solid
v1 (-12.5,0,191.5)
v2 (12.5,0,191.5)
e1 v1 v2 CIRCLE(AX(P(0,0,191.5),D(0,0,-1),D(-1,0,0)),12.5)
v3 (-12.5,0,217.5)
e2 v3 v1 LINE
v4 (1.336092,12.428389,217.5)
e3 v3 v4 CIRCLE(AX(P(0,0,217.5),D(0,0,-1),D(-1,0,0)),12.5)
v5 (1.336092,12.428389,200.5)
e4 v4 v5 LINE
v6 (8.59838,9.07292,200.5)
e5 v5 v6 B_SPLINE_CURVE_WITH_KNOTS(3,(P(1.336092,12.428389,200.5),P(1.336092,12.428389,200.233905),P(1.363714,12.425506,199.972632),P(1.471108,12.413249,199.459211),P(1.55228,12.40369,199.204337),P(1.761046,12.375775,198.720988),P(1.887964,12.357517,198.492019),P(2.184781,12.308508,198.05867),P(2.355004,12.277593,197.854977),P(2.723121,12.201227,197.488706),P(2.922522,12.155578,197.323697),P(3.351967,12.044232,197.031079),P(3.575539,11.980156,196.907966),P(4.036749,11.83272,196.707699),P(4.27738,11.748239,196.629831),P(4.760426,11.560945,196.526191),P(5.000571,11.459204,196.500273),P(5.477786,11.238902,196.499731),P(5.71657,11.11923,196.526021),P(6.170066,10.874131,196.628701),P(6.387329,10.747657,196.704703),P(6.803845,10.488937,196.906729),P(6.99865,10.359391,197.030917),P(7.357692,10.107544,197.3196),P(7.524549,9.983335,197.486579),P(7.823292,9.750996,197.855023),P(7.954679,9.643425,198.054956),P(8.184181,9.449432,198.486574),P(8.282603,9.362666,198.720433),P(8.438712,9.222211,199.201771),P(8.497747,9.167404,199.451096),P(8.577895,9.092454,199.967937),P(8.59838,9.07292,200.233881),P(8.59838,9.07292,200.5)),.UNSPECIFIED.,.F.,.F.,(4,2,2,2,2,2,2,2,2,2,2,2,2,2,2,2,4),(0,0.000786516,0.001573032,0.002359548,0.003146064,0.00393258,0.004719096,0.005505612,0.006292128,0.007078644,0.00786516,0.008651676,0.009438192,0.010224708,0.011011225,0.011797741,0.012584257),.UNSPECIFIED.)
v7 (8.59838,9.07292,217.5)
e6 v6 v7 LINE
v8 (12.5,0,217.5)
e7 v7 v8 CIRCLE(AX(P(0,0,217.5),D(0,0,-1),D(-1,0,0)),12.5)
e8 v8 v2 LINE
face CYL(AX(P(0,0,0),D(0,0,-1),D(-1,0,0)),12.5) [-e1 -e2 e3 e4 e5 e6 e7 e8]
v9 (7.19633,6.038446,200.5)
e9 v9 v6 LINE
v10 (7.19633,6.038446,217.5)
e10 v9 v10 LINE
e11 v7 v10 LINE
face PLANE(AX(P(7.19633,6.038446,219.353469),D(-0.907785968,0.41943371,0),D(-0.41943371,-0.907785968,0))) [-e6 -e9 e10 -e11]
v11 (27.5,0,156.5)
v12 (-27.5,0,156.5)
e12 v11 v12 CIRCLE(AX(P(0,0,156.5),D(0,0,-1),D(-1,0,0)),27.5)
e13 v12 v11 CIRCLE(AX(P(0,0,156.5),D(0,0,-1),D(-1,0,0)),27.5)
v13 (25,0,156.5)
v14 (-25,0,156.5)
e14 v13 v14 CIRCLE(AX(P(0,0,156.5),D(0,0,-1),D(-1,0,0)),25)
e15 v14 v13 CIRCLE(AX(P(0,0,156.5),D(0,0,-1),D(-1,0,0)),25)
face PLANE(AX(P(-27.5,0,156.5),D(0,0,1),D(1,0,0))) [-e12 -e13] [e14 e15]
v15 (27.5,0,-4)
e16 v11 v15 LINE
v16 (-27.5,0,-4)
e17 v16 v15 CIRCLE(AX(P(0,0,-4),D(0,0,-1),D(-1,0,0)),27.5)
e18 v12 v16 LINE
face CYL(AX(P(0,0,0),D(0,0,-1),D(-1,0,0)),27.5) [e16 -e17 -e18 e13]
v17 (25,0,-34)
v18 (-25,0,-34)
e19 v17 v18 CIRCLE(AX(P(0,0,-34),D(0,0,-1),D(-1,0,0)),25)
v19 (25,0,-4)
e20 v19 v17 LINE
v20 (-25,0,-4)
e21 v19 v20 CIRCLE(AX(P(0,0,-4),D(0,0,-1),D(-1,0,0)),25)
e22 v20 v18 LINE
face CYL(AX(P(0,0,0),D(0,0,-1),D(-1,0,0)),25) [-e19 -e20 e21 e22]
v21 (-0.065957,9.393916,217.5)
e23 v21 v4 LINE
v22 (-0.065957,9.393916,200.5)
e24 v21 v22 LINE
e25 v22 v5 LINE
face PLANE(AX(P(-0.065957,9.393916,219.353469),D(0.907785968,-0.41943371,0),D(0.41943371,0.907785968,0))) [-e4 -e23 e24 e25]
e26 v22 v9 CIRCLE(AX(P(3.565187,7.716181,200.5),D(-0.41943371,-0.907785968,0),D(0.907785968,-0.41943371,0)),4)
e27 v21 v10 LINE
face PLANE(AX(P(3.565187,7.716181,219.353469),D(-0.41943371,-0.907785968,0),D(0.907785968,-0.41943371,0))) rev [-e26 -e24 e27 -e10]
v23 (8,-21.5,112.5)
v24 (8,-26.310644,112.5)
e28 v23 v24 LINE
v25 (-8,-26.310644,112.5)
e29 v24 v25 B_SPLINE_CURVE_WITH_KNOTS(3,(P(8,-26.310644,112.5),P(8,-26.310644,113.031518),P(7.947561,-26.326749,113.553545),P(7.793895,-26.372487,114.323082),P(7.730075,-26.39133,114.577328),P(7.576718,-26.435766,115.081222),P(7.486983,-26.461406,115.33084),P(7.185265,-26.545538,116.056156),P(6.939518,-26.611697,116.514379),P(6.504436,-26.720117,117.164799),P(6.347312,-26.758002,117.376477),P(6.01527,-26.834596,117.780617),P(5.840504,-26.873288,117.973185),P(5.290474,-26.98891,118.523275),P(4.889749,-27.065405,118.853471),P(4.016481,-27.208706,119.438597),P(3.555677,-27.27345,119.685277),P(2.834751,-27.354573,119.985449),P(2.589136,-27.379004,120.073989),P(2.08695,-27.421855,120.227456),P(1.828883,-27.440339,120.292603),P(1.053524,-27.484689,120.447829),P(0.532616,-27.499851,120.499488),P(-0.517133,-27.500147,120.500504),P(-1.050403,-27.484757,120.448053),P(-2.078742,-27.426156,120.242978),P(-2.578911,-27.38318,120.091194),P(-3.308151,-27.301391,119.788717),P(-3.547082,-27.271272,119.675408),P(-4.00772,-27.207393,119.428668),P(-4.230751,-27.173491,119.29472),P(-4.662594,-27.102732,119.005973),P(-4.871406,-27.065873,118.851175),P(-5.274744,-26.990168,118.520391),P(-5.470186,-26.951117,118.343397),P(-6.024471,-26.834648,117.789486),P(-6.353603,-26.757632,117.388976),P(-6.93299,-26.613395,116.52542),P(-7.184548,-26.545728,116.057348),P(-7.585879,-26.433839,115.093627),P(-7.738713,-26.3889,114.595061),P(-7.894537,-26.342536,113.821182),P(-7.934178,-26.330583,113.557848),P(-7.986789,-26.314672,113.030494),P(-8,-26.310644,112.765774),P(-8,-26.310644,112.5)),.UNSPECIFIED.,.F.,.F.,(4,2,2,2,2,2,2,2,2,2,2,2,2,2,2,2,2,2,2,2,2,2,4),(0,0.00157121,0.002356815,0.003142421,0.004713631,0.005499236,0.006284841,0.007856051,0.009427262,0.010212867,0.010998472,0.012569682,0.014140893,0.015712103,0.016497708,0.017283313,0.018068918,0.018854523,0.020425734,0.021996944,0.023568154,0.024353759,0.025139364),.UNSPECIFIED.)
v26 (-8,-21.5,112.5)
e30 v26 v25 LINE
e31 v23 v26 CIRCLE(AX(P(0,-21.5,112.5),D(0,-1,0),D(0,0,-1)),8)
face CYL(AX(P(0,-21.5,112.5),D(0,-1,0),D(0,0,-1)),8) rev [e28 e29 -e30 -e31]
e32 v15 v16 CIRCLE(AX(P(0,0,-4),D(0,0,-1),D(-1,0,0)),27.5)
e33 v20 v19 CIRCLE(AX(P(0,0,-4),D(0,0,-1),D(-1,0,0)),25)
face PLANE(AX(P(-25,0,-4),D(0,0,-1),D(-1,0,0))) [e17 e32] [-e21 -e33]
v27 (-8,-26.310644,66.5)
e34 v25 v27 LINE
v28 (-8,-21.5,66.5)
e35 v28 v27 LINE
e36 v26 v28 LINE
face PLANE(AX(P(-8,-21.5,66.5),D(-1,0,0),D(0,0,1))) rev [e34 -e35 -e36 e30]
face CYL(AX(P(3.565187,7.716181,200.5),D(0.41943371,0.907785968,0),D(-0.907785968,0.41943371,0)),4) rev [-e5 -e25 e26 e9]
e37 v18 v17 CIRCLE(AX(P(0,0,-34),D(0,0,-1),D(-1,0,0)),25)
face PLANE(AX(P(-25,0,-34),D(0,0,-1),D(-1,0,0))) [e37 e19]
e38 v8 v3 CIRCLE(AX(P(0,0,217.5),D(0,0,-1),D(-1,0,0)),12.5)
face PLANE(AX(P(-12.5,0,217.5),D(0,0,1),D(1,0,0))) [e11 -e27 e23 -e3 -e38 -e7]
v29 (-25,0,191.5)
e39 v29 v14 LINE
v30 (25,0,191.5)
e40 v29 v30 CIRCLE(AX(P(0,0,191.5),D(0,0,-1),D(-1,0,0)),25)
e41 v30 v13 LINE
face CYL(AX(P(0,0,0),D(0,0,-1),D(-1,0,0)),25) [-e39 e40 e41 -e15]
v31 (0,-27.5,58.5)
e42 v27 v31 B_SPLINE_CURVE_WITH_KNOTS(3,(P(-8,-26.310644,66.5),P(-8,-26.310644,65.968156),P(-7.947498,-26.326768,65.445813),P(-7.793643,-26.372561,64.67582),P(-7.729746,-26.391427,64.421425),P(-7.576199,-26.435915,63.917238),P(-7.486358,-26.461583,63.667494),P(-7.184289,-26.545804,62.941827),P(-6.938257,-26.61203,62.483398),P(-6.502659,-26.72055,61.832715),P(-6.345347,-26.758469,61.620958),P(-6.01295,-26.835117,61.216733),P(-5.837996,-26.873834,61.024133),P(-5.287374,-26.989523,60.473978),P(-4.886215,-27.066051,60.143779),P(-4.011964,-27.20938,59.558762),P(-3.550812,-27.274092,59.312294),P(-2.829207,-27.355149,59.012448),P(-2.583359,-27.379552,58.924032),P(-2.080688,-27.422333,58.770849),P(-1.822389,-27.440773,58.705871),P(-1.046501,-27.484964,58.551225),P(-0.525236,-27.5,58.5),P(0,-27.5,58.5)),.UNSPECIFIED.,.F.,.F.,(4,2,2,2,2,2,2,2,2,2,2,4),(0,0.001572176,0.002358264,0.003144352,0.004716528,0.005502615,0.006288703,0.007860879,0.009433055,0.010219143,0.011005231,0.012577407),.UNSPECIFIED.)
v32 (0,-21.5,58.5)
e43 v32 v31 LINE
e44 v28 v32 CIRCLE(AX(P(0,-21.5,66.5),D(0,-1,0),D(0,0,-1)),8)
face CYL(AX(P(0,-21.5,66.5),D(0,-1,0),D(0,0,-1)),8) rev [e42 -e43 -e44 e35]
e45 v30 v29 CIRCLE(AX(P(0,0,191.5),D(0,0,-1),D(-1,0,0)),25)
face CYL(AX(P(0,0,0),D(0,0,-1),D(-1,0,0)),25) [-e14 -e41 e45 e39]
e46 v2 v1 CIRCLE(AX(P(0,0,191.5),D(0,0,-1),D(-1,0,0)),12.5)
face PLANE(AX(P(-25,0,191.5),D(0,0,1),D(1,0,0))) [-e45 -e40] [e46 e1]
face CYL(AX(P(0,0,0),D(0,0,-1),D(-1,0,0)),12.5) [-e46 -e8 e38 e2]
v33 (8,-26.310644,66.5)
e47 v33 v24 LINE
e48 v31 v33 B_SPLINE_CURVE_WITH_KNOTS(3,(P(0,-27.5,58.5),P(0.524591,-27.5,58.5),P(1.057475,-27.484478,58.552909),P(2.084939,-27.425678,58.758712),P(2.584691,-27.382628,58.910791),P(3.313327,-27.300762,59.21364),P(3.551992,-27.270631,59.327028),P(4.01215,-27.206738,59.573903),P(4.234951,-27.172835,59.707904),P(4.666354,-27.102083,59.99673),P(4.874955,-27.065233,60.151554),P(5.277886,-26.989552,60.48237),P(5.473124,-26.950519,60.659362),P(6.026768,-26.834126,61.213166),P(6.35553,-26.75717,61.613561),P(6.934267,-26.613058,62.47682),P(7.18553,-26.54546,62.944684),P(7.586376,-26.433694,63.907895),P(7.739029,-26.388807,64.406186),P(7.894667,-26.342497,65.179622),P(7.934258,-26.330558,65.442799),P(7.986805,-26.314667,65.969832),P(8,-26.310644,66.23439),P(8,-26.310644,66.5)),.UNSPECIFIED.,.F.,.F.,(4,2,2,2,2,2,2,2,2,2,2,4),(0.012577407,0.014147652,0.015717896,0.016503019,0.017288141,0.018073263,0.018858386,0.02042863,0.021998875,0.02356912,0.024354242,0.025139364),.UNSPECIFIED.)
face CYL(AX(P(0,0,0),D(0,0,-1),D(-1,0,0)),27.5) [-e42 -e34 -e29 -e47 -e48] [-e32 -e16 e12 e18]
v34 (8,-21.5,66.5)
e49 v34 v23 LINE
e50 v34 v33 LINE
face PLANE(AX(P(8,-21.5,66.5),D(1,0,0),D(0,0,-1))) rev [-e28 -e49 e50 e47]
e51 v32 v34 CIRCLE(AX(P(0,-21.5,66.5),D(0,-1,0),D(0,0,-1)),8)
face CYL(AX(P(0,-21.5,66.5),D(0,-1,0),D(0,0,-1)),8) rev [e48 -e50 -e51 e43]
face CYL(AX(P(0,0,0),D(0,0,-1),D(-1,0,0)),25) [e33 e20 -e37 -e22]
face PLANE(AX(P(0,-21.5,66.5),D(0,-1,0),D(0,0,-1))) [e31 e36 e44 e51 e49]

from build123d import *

# Parameters (mm, degrees)
CUT_EXTRUDE_2_DEPTH = 6
CUT_EXTRUDE_3_DEPTH = 7.3


with BuildPart() as part:
    # 草图1 → 旋转1 (revolve)
    with BuildSketch(Plane(origin=(0, 0, 0), x_dir=(1, 0, 0), z_dir=(0, 1, 0))):
        Polygon((-25, 34), (-25, 4), (-27.5, 4), (-27.5, -156.5), (-25, -156.5), (-25, -191.5), (-12.5, -191.5), (-12.5, -217.5), (0, -217.5), (0, 34), align=None)
    revolve(axis=Axis((0, 0, 0), (0, 0, 1)))

    # 草图3 → 切除-拉伸2 (cut)
    with BuildSketch(Plane(origin=(0, -27.5, 0), x_dir=(-1, 0, 0), z_dir=(0, -1, 0))):
        with BuildLine():
            Line((8, -66.5), (8, -112.5))
            ThreePointArc((8, -112.5), (0, -120.5), (-8, -112.5))
            Line((-8, -112.5), (-8, -66.5))
            ThreePointArc((-8, -66.5), (0, -58.5), (8, -66.5))
        make_face()
    extrude(amount=-CUT_EXTRUDE_2_DEPTH, mode=Mode.SUBTRACT)

    # 草图4 → 切除-拉伸3 (cut)
    with BuildSketch(Plane(origin=(6.627052614, 14.343018289, 0), x_dir=(0.9077859676868876, -0.41943370974539124, 0), z_dir=(-0.4194337097453913, -0.9077859676868877, 0))):
        with BuildLine():
            Line((4, 219.353468604), (4, 200.5))
            ThreePointArc((4, 200.5), (0, 196.5), (-4, 200.5))
            Line((-4, 200.5), (-4, 219.353468604))
            ThreePointArc((-4, 219.353468604), (0, 223.353468604), (4, 219.353468604))
        make_face()
    extrude(amount=CUT_EXTRUDE_3_DEPTH, mode=Mode.SUBTRACT)


solid = part.part
